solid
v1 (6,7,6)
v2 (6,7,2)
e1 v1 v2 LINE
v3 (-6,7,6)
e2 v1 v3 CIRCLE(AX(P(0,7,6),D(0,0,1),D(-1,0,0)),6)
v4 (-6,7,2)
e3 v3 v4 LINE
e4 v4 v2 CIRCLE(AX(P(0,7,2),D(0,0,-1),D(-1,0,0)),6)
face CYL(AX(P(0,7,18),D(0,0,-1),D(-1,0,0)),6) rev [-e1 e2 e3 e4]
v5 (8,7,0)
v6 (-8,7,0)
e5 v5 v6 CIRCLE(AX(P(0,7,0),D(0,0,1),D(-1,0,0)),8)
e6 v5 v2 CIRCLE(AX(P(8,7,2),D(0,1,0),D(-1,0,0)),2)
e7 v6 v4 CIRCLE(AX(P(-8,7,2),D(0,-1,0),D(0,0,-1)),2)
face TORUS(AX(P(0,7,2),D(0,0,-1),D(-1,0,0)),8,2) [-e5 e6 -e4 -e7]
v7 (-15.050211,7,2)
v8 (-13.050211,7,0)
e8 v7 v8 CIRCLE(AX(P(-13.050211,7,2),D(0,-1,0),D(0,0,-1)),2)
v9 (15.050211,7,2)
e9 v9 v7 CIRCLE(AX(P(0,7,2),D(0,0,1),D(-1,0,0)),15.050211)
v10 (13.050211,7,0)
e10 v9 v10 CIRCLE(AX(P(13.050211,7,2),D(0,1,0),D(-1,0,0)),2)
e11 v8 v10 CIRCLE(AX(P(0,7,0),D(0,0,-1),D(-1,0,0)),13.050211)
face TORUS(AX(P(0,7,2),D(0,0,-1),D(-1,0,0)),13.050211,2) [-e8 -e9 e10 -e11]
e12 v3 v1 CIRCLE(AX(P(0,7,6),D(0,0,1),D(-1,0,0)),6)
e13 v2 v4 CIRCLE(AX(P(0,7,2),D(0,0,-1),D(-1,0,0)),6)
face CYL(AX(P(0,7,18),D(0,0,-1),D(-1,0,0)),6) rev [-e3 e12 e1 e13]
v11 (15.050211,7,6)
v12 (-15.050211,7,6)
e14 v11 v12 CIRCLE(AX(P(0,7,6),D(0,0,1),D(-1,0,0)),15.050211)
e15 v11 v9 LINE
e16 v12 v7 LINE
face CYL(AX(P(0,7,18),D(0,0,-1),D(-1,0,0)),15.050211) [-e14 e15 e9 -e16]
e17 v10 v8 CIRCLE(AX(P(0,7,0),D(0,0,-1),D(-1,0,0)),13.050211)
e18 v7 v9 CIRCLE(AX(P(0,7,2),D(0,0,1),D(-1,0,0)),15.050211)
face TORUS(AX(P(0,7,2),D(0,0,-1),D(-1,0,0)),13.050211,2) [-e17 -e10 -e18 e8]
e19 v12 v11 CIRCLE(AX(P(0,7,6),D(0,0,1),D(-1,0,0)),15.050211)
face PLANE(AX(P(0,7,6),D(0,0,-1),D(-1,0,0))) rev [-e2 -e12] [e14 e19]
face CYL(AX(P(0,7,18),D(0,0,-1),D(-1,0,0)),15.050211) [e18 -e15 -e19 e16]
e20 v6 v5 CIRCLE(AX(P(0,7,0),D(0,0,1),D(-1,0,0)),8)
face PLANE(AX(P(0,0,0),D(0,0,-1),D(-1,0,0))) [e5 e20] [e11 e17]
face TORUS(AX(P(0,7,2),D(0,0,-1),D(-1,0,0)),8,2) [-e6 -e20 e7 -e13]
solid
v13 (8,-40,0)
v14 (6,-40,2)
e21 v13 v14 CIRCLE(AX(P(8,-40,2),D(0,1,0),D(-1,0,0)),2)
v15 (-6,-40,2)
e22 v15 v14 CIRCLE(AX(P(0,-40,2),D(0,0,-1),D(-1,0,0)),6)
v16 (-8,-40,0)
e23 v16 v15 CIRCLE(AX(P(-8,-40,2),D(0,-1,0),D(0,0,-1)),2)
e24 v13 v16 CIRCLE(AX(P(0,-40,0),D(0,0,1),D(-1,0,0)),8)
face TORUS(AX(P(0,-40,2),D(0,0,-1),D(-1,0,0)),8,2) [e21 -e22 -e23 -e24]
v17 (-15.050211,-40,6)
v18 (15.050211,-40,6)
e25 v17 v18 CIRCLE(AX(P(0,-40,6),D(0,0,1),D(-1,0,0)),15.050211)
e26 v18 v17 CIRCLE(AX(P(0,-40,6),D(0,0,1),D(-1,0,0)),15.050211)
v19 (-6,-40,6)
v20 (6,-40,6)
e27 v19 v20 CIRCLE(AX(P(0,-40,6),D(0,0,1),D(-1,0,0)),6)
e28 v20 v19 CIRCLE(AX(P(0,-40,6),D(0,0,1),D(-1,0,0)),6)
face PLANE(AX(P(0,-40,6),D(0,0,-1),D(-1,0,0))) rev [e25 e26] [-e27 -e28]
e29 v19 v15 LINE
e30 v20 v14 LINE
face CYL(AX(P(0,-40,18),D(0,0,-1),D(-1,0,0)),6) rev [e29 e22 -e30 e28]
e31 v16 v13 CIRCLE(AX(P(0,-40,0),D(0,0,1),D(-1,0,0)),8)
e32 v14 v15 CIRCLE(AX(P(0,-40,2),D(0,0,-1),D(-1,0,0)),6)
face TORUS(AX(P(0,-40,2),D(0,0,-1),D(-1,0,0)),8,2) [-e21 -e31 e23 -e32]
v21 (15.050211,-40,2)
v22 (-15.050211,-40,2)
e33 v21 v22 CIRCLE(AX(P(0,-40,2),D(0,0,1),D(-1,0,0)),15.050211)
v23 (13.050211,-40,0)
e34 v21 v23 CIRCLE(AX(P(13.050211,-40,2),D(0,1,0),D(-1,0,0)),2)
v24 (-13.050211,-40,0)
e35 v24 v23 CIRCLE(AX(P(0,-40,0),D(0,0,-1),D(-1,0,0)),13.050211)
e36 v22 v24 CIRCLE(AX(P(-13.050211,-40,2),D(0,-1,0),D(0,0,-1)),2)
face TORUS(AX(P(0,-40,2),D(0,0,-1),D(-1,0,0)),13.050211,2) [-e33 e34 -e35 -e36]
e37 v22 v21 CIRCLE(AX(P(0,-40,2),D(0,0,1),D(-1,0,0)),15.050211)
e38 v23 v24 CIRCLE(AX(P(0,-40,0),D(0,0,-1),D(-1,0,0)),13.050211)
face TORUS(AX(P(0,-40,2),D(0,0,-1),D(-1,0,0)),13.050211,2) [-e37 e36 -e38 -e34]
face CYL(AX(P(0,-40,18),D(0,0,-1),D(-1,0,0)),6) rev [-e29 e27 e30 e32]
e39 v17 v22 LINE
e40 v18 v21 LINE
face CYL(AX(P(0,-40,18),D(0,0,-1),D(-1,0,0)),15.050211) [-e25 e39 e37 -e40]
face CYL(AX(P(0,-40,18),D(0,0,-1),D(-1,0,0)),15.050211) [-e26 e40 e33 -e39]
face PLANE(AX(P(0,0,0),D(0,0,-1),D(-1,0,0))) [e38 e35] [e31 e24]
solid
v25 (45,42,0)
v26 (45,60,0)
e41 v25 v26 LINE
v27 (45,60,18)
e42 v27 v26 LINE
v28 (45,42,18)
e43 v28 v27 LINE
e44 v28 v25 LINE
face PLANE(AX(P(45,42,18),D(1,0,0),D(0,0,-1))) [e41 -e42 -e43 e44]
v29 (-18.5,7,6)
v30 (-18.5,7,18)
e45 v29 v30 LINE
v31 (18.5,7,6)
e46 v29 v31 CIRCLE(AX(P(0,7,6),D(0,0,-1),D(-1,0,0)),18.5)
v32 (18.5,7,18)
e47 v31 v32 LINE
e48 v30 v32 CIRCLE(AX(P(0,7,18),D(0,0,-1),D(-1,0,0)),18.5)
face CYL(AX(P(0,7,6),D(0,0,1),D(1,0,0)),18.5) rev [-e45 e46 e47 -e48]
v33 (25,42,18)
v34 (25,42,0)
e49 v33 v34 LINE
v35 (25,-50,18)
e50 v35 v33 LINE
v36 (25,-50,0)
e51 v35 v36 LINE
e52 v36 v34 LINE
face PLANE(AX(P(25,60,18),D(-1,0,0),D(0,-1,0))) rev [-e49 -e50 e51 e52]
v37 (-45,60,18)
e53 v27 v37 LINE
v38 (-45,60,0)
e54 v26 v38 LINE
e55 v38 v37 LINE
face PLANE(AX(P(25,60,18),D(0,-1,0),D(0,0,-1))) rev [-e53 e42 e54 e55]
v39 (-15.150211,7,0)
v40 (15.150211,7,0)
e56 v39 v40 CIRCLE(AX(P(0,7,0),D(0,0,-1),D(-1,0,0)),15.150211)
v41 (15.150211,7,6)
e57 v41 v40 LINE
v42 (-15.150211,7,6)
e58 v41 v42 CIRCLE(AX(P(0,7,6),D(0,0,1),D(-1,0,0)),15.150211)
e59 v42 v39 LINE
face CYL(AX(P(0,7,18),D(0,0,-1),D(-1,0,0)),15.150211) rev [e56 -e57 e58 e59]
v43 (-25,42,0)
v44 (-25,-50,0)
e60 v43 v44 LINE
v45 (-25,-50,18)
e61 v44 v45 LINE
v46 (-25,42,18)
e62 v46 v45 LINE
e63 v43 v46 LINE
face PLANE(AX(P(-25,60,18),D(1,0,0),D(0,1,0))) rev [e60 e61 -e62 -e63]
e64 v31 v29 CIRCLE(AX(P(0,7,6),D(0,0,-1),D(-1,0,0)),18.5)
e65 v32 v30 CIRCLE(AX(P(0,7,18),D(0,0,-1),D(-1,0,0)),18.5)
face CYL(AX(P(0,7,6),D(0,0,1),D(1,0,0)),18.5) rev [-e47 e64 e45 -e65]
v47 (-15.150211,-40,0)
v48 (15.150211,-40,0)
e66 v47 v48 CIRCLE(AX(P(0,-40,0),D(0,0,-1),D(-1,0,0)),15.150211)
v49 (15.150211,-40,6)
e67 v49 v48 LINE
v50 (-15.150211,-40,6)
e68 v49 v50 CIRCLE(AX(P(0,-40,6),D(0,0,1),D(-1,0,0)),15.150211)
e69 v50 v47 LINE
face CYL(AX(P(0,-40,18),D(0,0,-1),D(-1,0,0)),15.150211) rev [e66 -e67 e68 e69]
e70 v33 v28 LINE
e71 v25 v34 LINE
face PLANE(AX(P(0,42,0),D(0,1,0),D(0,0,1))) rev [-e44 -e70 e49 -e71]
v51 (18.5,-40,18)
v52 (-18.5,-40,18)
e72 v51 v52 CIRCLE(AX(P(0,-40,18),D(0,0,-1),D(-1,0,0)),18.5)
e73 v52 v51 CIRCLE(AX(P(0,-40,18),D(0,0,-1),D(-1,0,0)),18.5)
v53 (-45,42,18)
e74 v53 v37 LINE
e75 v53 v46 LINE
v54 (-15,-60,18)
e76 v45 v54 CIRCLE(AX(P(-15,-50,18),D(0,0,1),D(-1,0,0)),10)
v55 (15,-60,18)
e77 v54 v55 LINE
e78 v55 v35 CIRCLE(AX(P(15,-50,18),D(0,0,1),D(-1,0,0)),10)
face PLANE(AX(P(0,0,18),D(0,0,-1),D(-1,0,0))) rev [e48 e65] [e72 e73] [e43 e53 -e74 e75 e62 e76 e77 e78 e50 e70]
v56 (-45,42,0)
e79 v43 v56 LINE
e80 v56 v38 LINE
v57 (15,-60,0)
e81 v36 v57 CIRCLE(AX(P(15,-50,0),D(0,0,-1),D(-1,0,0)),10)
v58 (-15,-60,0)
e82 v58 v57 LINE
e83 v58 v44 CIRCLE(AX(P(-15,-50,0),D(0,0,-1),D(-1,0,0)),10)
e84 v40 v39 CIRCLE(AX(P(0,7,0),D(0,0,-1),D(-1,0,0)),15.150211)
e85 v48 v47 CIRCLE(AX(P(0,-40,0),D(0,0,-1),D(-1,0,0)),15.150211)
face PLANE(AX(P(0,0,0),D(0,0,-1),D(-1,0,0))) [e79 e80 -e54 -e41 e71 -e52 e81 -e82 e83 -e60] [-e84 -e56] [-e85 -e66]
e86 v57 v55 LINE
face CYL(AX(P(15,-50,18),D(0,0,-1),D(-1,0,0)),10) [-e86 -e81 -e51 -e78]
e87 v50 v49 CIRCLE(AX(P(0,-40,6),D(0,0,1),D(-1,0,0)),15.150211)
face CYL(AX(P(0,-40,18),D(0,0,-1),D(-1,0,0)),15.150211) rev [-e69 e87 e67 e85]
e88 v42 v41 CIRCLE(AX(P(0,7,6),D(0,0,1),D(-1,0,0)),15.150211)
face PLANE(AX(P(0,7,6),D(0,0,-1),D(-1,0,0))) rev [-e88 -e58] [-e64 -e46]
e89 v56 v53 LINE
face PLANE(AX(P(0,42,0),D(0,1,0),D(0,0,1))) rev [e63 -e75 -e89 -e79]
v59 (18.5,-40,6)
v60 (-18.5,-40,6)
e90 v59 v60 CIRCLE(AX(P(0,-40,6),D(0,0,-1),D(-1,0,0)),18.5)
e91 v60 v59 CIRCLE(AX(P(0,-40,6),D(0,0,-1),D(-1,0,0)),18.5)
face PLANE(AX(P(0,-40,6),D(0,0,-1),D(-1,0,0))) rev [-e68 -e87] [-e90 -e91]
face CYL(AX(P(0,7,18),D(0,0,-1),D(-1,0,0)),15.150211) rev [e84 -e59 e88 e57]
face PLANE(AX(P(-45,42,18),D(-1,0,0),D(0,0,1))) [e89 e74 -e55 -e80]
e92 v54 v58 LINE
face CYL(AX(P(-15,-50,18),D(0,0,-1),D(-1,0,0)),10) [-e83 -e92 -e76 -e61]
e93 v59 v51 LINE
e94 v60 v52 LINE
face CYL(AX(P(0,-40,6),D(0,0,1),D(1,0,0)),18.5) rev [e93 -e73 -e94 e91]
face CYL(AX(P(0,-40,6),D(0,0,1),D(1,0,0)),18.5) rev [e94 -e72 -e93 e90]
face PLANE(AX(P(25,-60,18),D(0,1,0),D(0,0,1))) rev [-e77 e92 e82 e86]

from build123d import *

# Parameters (mm, degrees)
SKETCH_1_W             = 50
SKETCH_1_H             = 120
EXTRUDE_1_DEPTH        = 18
SKETCH_2_W             = 90
SKETCH_2_H             = 18
EXTRUDE_2_DEPTH        = 18
FILLET_1_R             = 10
SKETCH_3_R             = 6
CUT_EXTRUDE_1_DEPTH    = 78.129760793
SKETCH_4_R             = 15.150210707
SKETCH_4_R_2           = 15.050210707
CUT_EXTRUDE_2_DEPTH    = 78.129760793
PATTERN_LINEAR_1_COUNT = 2
PATTERN_LINEAR_1_PITCH = 47
FILLET_2_R             = 2
FILLET_3_R             = 2
SKETCH_5_R             = 18.5
CUT_EXTRUDE_3_DEPTH    = 12


with BuildPart() as part:
    # 草图1 → 凸台-拉伸1 (new body)
    with BuildSketch(Plane.XY):
        Rectangle(SKETCH_1_W, SKETCH_1_H)
    extrude(amount=EXTRUDE_1_DEPTH)

    # 草图2 → 凸台-拉伸2 (add)
    with BuildSketch(Plane(origin=(0, 60, 0), x_dir=(1, 0, 0), z_dir=(0, 1, 0))):
        with Locations((0, -9)):
            Rectangle(SKETCH_2_W, SKETCH_2_H)
    extrude(amount=-EXTRUDE_2_DEPTH)

    # 圆角1
    fillet_1_edges = [part.edges().sort_by_distance(p)[0] for p in [
        (25, -60, 9),
        (-25, -60, 9),
    ]]
    fillet(fillet_1_edges, radius=FILLET_1_R)

    # 草图3 → 切除-拉伸1 (cut, through all)
    with BuildSketch(Plane(origin=(0, 0, 0), x_dir=(-1, 0, 0), z_dir=(0, 0, -1))):
        with Locations((0, -40)):
            Circle(SKETCH_3_R)
    cut_extrude_1 = extrude(amount=-CUT_EXTRUDE_1_DEPTH, mode=Mode.SUBTRACT)

    # 草图4 → 切除-拉伸2 (cut, through all)
    with BuildSketch(Plane(origin=(0, 0, 0), x_dir=(-1, 0, 0), z_dir=(0, 0, -1))):
        with Locations((0, -40)):
            Circle(SKETCH_4_R)
        with Locations((0, -40)):
            Circle(SKETCH_4_R_2, mode=Mode.SUBTRACT)
    cut_extrude_2 = extrude(amount=-CUT_EXTRUDE_2_DEPTH, mode=Mode.SUBTRACT)


with BuildPart() as cut_extrude_2_piece_1:
    # of the separate pieces the step leaves, piece 1, a body of its own (cut_extrude_2_pieces)
    add(part.part.solids().sort_by_distance((-25, -50, 0))[0])

    # 阵列(线性)1: 切除-拉伸1, 切除-拉伸2 ×2
    with Locations(*[(0, i * PATTERN_LINEAR_1_PITCH, 0) for i in range(1, PATTERN_LINEAR_1_COUNT)]):
        add(cut_extrude_1, mode=Mode.SUBTRACT)
        add(cut_extrude_2, mode=Mode.SUBTRACT)

    # 圆角3
    fillet_3_edges = [cut_extrude_2_piece_1.edges().sort_by_distance(p)[0] for p in [
        (6, 7, 18),
        (6, 7, 0),
        (15.050210707, 7, 18),
        (15.050210707, 7, 0),
    ]]
    fillet(fillet_3_edges, radius=FILLET_3_R)


with BuildPart() as cut_extrude_2_piece_2:
    # of the separate pieces the step leaves, piece 2, a body of its own (cut_extrude_2_pieces)
    add(part.part.solids().sort_by_distance((-15.050210707, -40, 0))[0])

    # 圆角2
    fillet_2_edges = [cut_extrude_2_piece_2.edges().sort_by_distance(p)[0] for p in [
        (6, -40, 18),
        (6, -40, 0),
        (15.050210707, -40, 18),
        (15.050210707, -40, 0),
    ]]
    fillet(fillet_2_edges, radius=FILLET_2_R)


with BuildPart() as cut_extrude_3_tool:
    # 草图5 → 切除-拉伸3 (new body)
    with BuildSketch(Plane(origin=(0, 0, 18), x_dir=(-1, 0, 0), z_dir=(0, 0, -1))):
        with Locations((0, -40)):
            Circle(SKETCH_5_R)
        with Locations((0, 7)):
            Circle(SKETCH_5_R)
    extrude(amount=CUT_EXTRUDE_3_DEPTH)


with BuildPart() as cut_extrude_2_piece_1_1:
    add(cut_extrude_2_piece_1.part)

    # 切除-拉伸3: cut by cut_extrude_3_tool
    add(cut_extrude_3_tool.part, mode=Mode.SUBTRACT)


with BuildPart() as cut_extrude_2_piece_2_1:
    add(cut_extrude_2_piece_2.part)

    # 切除-拉伸3: cut by cut_extrude_3_tool
    add(cut_extrude_3_tool.part, mode=Mode.SUBTRACT)


solid = Compound([cut_extrude_2_piece_1_1.part, cut_extrude_2_piece_2_1.part])
